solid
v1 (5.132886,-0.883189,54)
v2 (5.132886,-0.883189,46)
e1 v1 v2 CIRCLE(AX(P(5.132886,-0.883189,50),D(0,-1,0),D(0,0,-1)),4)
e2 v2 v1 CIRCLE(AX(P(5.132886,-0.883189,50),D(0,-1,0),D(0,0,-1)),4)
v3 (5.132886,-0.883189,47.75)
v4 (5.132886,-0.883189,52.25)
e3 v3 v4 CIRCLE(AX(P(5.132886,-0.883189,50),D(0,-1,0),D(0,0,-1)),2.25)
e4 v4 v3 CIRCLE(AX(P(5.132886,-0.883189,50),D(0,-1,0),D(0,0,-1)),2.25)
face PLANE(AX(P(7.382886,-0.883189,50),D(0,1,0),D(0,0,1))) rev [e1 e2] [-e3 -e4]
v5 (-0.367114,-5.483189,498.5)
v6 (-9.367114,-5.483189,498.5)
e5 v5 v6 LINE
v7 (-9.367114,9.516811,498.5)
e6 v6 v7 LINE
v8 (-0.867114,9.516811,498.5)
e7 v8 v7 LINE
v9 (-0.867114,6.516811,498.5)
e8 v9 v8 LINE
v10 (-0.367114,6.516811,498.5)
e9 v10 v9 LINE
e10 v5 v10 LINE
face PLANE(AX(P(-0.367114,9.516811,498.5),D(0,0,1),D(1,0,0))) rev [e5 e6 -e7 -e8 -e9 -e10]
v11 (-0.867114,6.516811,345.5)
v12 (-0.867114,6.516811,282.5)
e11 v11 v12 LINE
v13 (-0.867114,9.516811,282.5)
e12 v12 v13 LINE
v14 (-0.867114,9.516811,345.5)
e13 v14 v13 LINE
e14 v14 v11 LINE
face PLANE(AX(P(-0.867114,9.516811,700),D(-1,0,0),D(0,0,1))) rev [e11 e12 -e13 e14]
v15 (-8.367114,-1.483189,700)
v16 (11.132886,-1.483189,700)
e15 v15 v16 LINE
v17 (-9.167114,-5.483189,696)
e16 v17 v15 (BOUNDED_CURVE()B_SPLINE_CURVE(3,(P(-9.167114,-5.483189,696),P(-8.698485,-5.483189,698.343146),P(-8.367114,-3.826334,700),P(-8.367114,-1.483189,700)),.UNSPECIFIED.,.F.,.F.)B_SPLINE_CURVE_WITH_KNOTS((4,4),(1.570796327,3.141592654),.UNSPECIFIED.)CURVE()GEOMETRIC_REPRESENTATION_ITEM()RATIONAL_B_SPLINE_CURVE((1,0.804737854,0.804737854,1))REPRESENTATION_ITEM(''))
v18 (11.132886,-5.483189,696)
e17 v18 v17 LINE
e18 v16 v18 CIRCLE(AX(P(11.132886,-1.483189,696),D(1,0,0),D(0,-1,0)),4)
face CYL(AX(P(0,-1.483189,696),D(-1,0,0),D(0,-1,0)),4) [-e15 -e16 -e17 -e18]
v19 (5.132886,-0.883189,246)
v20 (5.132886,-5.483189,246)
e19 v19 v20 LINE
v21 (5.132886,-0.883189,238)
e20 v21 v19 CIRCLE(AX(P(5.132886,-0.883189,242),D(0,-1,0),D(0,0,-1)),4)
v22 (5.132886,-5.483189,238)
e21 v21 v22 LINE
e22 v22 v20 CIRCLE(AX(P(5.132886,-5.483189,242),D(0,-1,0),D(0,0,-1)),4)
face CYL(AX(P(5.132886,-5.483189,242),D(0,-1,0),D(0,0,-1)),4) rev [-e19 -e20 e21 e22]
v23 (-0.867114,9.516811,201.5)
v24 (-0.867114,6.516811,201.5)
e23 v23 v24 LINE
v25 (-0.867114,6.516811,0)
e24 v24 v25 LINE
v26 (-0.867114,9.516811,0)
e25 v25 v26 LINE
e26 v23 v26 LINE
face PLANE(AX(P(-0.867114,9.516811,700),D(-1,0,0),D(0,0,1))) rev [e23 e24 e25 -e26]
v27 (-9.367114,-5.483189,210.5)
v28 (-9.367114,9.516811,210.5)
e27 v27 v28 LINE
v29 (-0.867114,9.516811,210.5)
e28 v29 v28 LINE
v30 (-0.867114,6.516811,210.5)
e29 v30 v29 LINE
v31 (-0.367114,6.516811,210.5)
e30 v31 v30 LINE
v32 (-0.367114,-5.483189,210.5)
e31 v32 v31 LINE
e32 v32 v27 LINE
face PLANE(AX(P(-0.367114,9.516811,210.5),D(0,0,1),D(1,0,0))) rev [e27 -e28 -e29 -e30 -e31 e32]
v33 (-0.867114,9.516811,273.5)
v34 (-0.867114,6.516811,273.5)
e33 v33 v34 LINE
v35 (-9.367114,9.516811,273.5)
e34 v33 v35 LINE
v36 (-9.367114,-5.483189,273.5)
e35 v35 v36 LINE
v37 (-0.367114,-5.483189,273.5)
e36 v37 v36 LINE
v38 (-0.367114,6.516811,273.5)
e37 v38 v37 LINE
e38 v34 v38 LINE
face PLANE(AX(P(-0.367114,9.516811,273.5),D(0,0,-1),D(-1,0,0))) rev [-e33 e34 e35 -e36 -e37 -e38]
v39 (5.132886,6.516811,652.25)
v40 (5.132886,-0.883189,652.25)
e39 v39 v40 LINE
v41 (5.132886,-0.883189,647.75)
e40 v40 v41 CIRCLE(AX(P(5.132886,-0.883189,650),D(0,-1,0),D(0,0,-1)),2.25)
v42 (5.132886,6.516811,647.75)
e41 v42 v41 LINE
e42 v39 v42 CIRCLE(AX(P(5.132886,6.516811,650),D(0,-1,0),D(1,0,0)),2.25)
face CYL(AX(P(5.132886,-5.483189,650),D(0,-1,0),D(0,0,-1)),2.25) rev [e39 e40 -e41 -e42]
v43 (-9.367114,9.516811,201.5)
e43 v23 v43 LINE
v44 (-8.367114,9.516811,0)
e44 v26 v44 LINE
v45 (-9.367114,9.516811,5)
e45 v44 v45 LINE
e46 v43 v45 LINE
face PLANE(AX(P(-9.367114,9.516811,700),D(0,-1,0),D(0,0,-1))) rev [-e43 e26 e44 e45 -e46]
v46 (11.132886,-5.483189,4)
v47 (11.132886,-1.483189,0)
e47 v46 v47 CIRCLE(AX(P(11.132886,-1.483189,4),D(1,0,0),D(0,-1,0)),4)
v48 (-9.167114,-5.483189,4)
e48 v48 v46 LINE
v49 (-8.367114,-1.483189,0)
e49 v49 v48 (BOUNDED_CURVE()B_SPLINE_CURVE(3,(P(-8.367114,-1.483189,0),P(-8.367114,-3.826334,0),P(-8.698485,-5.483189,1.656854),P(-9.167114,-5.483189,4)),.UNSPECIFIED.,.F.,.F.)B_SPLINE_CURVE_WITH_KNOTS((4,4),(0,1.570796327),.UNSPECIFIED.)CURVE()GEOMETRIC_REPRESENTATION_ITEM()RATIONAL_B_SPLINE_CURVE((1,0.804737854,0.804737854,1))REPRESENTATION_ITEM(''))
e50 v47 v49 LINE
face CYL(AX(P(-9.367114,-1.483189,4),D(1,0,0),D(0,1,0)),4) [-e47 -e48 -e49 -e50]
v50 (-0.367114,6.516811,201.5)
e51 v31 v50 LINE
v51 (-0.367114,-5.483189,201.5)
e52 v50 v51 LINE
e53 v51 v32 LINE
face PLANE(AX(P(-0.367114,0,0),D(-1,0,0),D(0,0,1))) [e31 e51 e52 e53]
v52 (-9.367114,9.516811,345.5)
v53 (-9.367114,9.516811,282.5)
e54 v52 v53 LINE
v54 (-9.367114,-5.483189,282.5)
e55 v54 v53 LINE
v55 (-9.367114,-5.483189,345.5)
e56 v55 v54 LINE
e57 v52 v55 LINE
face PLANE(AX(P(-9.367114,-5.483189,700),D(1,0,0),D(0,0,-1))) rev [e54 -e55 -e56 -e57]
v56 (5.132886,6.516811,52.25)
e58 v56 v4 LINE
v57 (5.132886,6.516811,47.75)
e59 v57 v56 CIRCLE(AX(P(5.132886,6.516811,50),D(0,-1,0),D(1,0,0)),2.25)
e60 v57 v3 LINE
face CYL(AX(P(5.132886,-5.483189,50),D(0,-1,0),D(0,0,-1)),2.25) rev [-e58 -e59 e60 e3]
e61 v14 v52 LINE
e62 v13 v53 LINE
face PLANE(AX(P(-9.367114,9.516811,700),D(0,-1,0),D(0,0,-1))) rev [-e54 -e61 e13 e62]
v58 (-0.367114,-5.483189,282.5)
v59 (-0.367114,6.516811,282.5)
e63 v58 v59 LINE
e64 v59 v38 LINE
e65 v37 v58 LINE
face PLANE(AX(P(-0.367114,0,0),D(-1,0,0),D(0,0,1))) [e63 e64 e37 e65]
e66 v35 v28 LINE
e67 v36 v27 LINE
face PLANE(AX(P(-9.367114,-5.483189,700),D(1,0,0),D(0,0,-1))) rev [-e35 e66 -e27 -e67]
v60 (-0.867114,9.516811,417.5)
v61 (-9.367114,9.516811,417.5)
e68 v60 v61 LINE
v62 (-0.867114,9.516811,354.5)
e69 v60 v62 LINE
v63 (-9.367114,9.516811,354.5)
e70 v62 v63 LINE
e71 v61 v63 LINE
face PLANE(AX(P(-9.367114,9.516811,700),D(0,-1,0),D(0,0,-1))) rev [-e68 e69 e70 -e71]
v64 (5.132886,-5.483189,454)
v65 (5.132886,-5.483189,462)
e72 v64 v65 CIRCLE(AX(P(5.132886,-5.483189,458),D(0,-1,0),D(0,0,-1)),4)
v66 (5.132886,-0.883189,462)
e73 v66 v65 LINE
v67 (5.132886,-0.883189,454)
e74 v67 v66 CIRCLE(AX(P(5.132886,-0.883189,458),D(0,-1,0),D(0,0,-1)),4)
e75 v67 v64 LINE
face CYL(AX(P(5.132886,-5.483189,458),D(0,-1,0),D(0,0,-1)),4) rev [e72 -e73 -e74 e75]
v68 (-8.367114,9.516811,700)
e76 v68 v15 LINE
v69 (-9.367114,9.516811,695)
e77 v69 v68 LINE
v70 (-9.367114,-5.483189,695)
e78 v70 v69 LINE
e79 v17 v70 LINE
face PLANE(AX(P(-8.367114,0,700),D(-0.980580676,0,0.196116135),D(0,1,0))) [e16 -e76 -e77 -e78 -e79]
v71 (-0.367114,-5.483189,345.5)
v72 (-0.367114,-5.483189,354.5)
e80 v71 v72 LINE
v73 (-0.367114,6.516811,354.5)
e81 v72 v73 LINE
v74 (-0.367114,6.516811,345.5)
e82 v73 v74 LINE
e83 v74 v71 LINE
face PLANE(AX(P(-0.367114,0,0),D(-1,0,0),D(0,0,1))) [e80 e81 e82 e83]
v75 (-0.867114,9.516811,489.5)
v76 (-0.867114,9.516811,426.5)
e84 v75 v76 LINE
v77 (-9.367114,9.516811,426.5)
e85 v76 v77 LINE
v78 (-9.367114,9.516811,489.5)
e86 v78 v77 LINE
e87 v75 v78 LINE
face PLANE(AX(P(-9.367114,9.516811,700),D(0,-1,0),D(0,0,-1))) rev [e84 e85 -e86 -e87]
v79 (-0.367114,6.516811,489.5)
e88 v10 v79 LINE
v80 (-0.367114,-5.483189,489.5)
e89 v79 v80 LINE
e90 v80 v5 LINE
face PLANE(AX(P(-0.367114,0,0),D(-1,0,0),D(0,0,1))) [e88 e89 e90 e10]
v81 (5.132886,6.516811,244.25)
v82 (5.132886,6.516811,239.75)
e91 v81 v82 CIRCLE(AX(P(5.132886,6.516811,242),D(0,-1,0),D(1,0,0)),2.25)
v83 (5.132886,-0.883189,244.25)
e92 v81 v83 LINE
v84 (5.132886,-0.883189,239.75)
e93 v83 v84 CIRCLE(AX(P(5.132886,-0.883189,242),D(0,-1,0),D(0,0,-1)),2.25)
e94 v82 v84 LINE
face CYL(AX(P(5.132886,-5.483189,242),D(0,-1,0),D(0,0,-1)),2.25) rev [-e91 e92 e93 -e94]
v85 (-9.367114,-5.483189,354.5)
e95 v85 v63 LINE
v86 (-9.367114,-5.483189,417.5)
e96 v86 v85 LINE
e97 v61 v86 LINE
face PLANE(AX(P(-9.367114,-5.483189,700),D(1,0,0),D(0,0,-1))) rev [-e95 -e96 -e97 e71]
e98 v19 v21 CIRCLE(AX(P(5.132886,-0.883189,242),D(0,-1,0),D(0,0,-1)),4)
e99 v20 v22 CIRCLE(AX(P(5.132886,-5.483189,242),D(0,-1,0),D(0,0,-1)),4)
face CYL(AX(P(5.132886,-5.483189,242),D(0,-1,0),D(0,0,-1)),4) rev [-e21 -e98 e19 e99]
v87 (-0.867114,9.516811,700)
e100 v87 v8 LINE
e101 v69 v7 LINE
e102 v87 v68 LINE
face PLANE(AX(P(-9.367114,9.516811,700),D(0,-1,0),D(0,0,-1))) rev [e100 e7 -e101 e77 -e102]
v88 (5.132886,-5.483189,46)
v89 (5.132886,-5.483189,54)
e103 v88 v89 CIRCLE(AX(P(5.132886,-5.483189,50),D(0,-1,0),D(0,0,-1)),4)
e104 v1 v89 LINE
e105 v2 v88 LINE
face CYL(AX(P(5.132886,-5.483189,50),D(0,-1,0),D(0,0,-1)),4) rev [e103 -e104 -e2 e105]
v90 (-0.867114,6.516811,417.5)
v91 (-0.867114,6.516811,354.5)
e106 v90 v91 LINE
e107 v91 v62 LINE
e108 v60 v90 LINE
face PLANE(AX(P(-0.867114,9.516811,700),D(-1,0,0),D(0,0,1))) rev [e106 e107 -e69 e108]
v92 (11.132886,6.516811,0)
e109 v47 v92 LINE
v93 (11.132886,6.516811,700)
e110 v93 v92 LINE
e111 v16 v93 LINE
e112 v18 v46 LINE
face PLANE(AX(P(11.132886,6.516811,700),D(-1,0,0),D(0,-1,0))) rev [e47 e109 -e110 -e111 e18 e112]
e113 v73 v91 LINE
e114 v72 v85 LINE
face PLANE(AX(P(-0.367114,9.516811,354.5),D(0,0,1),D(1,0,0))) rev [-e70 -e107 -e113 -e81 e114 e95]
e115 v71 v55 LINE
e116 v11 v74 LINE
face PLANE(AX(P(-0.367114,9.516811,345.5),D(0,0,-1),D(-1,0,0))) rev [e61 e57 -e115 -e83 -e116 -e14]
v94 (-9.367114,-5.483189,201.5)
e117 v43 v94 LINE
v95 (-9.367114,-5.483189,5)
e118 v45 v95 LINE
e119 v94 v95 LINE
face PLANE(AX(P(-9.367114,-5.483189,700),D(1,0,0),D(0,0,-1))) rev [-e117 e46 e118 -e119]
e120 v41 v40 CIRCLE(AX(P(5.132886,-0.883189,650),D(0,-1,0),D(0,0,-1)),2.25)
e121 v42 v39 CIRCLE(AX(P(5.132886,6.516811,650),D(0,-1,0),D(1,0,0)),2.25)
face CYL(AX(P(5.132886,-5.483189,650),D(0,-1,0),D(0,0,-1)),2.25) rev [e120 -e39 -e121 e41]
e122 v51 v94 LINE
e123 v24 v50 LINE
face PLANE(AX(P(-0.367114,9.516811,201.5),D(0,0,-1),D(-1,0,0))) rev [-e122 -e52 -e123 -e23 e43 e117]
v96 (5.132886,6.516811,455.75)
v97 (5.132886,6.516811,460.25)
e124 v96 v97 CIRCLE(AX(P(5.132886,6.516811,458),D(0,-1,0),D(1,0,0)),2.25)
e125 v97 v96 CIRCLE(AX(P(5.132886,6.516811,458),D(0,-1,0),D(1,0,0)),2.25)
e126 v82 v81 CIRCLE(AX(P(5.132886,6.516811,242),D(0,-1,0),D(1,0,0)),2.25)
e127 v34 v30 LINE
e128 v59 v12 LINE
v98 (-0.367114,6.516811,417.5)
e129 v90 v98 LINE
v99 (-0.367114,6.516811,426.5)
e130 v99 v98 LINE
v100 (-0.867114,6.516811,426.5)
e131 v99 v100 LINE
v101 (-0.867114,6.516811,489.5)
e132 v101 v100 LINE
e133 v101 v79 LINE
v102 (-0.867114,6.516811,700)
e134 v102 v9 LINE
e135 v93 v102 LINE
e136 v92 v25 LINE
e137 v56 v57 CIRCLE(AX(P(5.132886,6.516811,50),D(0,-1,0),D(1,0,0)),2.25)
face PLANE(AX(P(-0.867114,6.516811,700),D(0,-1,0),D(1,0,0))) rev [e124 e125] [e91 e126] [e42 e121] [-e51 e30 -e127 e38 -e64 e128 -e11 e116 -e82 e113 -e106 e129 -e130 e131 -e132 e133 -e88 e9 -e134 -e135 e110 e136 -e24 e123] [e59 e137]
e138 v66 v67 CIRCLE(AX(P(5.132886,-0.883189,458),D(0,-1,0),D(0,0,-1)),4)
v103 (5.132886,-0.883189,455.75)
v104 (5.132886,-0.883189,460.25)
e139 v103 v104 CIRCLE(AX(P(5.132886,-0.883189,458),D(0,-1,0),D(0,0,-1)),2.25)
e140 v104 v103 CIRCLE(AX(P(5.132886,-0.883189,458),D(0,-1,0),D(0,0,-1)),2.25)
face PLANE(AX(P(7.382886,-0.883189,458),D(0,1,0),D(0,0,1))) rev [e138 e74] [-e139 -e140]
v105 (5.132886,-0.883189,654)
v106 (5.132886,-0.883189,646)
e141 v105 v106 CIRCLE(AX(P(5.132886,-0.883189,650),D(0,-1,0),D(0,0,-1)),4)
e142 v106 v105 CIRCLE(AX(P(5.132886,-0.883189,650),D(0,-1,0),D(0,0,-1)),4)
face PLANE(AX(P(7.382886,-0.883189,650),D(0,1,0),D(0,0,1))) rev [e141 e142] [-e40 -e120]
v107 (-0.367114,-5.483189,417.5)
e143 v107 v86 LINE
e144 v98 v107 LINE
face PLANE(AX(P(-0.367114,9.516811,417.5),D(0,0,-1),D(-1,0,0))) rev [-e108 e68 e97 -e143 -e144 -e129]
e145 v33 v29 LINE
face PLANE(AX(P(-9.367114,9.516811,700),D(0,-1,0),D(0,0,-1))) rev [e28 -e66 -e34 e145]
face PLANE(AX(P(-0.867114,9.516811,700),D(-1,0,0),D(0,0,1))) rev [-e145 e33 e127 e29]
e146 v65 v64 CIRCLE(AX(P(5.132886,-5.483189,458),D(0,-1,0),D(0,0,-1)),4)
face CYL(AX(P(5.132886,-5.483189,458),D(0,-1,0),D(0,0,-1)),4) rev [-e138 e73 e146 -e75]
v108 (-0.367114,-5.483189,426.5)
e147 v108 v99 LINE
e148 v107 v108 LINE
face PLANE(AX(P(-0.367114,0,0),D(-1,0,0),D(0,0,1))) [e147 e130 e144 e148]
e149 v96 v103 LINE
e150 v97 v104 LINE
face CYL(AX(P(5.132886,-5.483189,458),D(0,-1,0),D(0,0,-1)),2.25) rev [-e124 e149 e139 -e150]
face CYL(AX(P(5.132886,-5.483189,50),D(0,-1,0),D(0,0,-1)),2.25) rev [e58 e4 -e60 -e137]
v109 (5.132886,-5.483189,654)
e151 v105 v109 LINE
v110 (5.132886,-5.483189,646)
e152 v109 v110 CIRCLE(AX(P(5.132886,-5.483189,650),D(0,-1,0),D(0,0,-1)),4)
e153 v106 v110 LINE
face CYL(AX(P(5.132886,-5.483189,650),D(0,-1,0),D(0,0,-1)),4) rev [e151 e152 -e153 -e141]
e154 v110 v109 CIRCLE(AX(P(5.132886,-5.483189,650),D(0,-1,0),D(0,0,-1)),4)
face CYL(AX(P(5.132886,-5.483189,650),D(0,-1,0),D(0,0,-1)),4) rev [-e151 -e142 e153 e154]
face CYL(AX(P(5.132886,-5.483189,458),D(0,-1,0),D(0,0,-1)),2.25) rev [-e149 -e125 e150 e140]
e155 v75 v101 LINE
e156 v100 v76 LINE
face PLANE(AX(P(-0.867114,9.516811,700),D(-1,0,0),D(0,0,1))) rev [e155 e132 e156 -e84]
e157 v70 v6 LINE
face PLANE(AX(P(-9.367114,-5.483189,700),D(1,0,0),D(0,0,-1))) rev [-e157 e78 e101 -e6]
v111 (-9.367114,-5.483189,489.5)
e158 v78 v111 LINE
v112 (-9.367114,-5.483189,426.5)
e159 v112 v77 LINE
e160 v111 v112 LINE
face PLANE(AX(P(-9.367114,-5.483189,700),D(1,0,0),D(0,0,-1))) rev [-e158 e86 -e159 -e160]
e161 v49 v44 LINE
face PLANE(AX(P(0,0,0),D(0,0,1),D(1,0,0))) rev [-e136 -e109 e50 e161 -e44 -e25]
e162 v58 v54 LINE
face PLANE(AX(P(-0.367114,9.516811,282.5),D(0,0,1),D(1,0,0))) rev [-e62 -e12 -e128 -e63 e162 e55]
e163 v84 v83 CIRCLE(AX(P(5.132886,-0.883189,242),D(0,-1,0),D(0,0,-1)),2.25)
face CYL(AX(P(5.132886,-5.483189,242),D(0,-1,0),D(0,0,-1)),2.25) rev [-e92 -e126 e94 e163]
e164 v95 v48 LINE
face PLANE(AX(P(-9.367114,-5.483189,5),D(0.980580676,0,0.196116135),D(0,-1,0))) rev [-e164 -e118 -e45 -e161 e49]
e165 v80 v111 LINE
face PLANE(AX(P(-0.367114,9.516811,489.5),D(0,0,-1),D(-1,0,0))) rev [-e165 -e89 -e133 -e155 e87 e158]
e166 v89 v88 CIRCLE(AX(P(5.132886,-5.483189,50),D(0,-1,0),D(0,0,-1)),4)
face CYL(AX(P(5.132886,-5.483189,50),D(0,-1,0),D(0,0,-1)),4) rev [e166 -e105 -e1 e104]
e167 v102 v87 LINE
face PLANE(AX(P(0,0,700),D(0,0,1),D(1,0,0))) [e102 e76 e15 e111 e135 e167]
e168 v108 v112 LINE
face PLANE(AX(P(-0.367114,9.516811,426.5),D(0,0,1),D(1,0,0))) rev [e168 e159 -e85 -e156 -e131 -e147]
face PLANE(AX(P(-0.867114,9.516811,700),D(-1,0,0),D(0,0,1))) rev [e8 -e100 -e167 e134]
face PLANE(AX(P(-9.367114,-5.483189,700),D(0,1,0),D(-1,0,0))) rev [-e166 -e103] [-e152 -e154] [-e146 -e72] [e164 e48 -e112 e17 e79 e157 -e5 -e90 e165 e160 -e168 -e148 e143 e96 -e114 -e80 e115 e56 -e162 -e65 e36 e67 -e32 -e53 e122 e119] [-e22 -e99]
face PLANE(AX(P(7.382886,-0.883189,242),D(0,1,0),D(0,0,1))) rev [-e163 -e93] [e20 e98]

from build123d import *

# Parameters (mm, degrees)
EXTRUDE_1_DEPTH           = 700
HOLE_WIZARD_1_D           = 4.5
HOLE_WIZARD_1_CBORE_D     = 8
HOLE_WIZARD_1_CBORE_DEPTH = 4.6
SKETCH_5_W                = 9
SKETCH_5_H                = 15
CUT_EXTRUDE_1_DEPTH       = 9
CHAMFER_1_SIZE            = 5
CHAMFER_1_SIZE2           = 1
CHAMFER_2_SIZE            = 1
CHAMFER_2_SIZE2           = 5
FILLET_1_R                = 4


with BuildPart() as part:
    # 草图1 → 凸台-拉伸1 (new body)
    with BuildSketch(Plane.XY):
        Polygon((-9.367113838, -5.483188588), (11.132886162, -5.483188588), (11.132886162, 6.516811412), (-0.867113838, 6.516811412), (-0.867113838, 9.516811412), (-9.367113838, 9.516811412), align=None)
    extrude(amount=EXTRUDE_1_DEPTH)

    # 打孔尺寸根据内六角圆柱头螺钉的类型1 (through all)
    with Locations(Plane(origin=(0, -5.483188588, 0), x_dir=(-1, 0, 0), z_dir=(0, -1, 0))):
        with Locations((-5.132886162, -650), (-5.132886162, -458), (-5.132886162, -242), (-5.132886162, -50)):
            CounterBoreHole(HOLE_WIZARD_1_D / 2, HOLE_WIZARD_1_CBORE_D / 2, HOLE_WIZARD_1_CBORE_DEPTH)

    # 草图5 → 切除-拉伸1 (cut)
    with BuildSketch(Plane.ZY.offset(9.367113838)):
        with Locations((206, 2.016811412)):
            Rectangle(SKETCH_5_W, SKETCH_5_H)
        with Locations((278, 2.016811412)):
            Rectangle(SKETCH_5_W, SKETCH_5_H)
        with Locations((350, 2.016811412)):
            Rectangle(SKETCH_5_W, SKETCH_5_H)
        with Locations((422, 2.016811412)):
            Rectangle(SKETCH_5_W, SKETCH_5_H)
        with Locations((494, 2.016811412)):
            Rectangle(SKETCH_5_W, SKETCH_5_H)
    extrude(amount=-CUT_EXTRUDE_1_DEPTH, mode=Mode.SUBTRACT)

    # 倒角1
    chamfer_1_edges = [part.edges().sort_by_distance(p)[0] for p in [
        (-9.367113838, 2.016811412, 700),
    ]]
    chamfer_1_side = [part.faces().sort_by_distance(p)[0] for p in [
        (-9.367113838, 2.016811412, 599.25),
    ]]
    chamfer(chamfer_1_edges, length=CHAMFER_1_SIZE, length2=CHAMFER_1_SIZE2, reference=chamfer_1_side[0])

    # 倒角2
    chamfer_2_edges = [part.edges().sort_by_distance(p)[0] for p in [
        (-9.367113838, 2.016811412, 0),
    ]]
    chamfer_2_side = [part.faces().sort_by_distance(p)[0] for p in [
        (0.31935025, 1.221231301, 0),
    ]]
    chamfer(chamfer_2_edges, length=CHAMFER_2_SIZE, length2=CHAMFER_2_SIZE2, reference=chamfer_2_side[0])

    # 圆角1
    fillet_1_edges = [part.edges().sort_by_distance(p)[0] for p in [
        (1.382886162, -5.483188588, 700),
        (1.382886162, -5.483188588, 0),
    ]]
    fillet(fillet_1_edges, radius=FILLET_1_R)


solid = part.part
